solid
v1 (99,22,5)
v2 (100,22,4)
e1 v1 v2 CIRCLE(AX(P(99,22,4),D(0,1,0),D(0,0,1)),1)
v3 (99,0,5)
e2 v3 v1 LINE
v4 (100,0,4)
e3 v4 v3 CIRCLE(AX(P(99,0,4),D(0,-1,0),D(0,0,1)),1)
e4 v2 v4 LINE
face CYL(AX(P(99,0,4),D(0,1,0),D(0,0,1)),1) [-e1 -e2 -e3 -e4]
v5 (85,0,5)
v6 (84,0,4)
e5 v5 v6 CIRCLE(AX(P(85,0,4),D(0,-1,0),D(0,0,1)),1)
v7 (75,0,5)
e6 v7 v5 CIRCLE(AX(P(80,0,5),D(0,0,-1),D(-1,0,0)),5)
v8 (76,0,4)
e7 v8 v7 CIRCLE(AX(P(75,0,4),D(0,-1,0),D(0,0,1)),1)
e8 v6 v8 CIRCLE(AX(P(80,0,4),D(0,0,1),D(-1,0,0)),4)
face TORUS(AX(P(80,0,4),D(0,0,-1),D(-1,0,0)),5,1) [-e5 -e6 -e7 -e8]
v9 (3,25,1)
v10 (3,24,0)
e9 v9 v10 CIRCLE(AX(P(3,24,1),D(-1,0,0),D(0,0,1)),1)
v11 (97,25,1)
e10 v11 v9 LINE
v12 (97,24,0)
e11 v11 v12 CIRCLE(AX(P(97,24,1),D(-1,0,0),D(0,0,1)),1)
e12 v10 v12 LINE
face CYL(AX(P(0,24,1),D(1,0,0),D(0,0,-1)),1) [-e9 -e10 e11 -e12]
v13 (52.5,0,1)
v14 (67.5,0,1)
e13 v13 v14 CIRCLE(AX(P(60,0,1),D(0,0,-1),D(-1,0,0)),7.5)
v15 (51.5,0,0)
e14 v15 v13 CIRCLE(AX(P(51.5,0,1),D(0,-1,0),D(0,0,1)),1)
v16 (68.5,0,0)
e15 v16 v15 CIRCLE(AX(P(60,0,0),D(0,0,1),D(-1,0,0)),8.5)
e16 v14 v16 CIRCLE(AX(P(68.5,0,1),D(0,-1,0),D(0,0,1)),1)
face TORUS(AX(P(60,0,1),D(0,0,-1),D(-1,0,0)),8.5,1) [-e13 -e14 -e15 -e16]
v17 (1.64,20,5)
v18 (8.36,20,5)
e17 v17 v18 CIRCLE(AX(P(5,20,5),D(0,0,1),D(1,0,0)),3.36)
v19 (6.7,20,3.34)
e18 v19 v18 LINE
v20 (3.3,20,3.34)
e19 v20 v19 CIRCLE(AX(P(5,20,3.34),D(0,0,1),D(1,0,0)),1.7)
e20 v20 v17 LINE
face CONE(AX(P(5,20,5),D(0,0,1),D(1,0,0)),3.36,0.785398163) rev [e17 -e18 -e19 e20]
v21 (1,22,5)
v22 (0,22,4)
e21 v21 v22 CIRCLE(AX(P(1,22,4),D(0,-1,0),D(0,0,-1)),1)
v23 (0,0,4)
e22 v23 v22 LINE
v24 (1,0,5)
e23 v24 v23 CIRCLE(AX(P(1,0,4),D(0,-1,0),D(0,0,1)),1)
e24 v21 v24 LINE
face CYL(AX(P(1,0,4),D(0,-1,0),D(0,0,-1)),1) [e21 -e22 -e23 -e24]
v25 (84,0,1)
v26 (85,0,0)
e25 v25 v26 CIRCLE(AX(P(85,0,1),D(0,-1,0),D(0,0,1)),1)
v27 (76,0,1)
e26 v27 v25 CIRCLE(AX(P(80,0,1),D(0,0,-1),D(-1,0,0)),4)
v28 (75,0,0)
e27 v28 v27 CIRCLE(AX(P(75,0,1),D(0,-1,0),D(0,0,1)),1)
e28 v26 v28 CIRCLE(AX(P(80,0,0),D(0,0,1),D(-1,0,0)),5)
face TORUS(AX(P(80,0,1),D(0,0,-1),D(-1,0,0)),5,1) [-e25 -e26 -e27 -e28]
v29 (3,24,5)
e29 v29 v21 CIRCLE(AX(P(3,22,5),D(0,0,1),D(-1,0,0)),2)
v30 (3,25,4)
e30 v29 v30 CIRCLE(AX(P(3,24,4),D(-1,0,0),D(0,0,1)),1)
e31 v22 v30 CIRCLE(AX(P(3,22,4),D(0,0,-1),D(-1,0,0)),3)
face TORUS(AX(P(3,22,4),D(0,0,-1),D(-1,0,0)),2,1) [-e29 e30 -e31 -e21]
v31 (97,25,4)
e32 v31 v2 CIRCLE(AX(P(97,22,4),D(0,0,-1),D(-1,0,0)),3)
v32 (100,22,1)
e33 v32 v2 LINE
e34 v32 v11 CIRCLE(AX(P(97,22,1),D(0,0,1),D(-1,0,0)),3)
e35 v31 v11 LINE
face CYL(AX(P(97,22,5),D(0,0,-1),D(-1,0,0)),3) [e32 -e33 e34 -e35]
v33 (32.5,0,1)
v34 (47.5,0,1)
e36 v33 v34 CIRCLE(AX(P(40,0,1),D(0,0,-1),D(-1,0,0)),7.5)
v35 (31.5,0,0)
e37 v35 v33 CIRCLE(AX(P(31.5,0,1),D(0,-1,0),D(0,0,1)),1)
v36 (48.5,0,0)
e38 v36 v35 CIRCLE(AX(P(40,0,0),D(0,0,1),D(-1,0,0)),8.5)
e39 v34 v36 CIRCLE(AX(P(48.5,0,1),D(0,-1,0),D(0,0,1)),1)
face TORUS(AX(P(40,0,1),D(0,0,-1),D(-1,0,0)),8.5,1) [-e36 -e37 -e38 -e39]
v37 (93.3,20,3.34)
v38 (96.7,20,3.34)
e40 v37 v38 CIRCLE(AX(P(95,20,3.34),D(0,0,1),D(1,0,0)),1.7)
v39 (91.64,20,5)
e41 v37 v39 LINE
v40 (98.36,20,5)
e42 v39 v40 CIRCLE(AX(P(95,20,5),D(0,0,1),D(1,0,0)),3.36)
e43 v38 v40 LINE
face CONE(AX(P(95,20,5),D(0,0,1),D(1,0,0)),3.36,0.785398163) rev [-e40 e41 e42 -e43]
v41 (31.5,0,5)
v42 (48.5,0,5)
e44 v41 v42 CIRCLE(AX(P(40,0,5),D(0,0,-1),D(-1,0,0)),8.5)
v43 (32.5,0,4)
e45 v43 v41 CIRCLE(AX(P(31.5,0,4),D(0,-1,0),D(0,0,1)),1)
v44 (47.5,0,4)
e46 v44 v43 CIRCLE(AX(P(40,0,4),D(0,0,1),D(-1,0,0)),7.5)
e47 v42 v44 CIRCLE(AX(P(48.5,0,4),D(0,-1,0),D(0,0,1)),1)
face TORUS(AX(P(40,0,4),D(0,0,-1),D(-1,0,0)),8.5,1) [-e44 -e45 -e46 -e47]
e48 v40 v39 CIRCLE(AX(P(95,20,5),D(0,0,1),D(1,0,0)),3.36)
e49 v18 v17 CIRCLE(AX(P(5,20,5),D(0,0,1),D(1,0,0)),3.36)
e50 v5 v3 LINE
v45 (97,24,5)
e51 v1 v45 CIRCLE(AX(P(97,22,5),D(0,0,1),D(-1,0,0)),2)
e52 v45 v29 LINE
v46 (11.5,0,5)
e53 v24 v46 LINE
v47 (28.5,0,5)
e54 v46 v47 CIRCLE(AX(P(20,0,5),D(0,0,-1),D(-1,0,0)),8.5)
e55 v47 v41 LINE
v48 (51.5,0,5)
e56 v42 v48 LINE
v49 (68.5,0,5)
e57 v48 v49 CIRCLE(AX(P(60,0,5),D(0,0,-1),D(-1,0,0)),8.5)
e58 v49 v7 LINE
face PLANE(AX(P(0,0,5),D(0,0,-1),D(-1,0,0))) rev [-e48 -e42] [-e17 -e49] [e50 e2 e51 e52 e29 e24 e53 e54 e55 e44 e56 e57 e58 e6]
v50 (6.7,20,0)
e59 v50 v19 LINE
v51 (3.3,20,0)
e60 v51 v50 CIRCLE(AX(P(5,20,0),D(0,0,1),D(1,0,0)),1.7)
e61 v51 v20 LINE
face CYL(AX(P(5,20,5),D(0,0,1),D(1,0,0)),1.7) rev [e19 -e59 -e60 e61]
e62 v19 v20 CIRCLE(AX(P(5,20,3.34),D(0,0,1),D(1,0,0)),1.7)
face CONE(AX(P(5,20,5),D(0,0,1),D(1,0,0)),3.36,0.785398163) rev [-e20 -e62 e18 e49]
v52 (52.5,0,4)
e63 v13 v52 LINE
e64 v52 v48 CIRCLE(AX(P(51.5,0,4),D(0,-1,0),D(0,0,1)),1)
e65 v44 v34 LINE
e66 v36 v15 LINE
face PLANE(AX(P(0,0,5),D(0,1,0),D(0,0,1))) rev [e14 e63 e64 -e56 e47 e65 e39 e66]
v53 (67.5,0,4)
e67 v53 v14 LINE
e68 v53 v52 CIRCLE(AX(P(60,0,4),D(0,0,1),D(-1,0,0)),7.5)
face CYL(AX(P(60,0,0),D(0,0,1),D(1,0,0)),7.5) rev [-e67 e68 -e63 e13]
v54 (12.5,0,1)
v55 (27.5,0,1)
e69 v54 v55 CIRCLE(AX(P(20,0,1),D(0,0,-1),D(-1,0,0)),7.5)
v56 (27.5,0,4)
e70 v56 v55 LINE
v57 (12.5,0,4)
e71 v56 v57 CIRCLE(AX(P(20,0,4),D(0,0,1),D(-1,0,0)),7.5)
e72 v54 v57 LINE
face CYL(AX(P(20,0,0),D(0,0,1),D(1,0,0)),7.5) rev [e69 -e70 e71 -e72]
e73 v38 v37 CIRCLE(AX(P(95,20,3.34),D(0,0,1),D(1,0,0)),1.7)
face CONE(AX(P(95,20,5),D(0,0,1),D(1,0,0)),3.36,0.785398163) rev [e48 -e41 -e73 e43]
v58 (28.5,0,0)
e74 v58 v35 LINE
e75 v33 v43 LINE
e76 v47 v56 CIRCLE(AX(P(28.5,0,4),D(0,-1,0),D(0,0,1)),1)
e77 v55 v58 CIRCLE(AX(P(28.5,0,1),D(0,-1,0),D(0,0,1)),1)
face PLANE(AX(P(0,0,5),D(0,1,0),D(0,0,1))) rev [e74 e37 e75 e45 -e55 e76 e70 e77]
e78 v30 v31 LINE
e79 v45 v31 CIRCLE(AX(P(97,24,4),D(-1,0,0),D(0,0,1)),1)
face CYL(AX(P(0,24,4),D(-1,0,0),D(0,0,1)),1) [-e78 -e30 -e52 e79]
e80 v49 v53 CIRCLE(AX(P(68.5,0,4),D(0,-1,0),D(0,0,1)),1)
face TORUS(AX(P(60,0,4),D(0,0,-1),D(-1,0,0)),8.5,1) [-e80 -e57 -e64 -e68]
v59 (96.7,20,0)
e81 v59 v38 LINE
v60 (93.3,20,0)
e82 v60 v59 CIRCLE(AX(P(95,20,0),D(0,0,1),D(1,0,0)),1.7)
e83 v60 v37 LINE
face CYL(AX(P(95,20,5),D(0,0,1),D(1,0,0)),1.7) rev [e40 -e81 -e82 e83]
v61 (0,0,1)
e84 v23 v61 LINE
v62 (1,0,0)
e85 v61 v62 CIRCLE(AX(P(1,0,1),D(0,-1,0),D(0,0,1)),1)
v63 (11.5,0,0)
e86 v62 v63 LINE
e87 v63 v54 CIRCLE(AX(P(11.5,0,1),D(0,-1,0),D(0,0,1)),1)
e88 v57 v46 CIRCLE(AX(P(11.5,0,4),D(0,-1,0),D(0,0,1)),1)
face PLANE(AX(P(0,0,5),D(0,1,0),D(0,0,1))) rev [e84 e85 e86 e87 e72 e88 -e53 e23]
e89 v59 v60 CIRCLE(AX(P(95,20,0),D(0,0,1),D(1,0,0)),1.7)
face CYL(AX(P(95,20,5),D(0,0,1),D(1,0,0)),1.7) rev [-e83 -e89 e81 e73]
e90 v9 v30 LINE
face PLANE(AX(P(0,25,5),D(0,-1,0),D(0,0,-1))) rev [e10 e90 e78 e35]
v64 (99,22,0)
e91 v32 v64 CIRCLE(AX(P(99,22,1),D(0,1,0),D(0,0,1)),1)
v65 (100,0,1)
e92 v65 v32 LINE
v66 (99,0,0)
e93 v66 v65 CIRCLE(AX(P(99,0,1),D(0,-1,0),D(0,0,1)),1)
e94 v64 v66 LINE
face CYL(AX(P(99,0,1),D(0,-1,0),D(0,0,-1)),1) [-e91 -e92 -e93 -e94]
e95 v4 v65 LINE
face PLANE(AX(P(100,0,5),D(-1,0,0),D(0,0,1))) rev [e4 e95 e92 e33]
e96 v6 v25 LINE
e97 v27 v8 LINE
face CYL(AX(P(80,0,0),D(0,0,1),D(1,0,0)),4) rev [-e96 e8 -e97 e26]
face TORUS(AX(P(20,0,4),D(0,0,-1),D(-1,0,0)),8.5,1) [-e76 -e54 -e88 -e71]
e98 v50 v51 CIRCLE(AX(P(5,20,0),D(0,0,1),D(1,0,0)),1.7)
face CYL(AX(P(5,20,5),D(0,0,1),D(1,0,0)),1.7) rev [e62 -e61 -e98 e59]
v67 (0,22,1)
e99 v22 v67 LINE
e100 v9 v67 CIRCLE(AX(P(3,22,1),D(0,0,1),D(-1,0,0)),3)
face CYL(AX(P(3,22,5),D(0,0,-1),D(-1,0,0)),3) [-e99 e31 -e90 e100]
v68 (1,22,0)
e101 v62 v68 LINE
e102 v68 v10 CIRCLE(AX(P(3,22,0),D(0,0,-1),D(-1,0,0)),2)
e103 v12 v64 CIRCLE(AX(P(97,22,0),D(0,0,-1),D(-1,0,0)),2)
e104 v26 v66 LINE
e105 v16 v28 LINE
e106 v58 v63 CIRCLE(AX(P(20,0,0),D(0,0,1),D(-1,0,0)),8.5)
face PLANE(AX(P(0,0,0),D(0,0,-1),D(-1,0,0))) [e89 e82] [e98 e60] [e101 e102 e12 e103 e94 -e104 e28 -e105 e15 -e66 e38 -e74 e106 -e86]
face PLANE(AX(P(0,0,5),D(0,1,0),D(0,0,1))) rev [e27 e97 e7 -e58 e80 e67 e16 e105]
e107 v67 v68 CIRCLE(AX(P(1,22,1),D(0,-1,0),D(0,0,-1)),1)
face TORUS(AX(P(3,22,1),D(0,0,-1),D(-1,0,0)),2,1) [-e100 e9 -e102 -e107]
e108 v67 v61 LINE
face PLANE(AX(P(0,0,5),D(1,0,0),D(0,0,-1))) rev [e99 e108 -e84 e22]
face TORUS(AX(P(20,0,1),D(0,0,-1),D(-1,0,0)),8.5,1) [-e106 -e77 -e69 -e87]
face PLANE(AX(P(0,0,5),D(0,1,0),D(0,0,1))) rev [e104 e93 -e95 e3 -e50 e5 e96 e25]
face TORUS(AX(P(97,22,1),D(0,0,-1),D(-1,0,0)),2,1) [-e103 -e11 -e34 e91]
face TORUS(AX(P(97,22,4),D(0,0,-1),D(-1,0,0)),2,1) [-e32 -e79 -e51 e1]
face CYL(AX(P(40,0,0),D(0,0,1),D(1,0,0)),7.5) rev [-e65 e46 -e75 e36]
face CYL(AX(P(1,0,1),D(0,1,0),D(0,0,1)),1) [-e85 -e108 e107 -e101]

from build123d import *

# Parameters (mm, degrees)
SKETCH_1_W                   = 100
SKETCH_1_H                   = 25
EXTRUDE_1_DEPTH              = 5
SKETCH_2_R                   = 7.5
SKETCH_2_R_2                 = 4
CUT_EXTRUDE_1_DEPTH          = 104.198837203
HOLE_WIZARD_M3_1_D           = 3.4
HOLE_WIZARD_M3_1_CSINK_D     = 6.72
HOLE_WIZARD_M3_1_CSINK_ANGLE = 90
FILLET_1_R                   = 3
FILLET_2_R                   = 1


with BuildPart() as part:
    # 草图1 → 凸台-拉伸1 (new body)
    with BuildSketch(Plane.XY):
        with Locations((50, 12.5)):
            Rectangle(SKETCH_1_W, SKETCH_1_H)
    extrude(amount=EXTRUDE_1_DEPTH)

    # 草图2 → 切除-拉伸1 (cut, through all)
    with BuildSketch(Plane.XY.offset(5)):
        with Locations((20, 0)):
            Circle(SKETCH_2_R)
        with Locations((40, 0)):
            Circle(SKETCH_2_R)
        with Locations((60, 0)):
            Circle(SKETCH_2_R)
        with Locations((80, 0)):
            Circle(SKETCH_2_R_2)
    extrude(amount=-CUT_EXTRUDE_1_DEPTH, mode=Mode.SUBTRACT)

    # M3 六角凹锥坑螺钉的锥形沉头孔1 (through all)
    with Locations(Plane.XY.offset(5)):
        with Locations((5, 20), (95, 20)):
            CounterSinkHole(HOLE_WIZARD_M3_1_D / 2, HOLE_WIZARD_M3_1_CSINK_D / 2, counter_sink_angle=HOLE_WIZARD_M3_1_CSINK_ANGLE)

    # 圆角1
    fillet_1_edges = [part.edges().sort_by_distance(p)[0] for p in [
        (0, 25, 2.5),
        (100, 25, 2.5),
    ]]
    fillet(fillet_1_edges, radius=FILLET_1_R)

    # 圆角2
    fillet_2_edges = [part.edges().sort_by_distance(p)[0] for p in [
        (100, 11, 5),
        (20, 7.5, 5),
        (20, 7.5, 0),
        (40, 7.5, 5),
        (40, 7.5, 0),
        (60, 7.5, 5),
        (60, 7.5, 0),
        (80, 4, 5),
        (80, 4, 0),
        (100, 11, 0),
        (50, 25, 0),
        (50, 25, 5),
        (0, 11, 0),
        (0.878679656, 24.121320344, 0),
        (99.121320344, 24.121320344, 0),
        (0, 11, 5),
        (0.878679656, 24.121320344, 5),
        (99.121320344, 24.121320344, 5),
    ]]
    fillet(fillet_2_edges, radius=FILLET_2_R)


solid = part.part
